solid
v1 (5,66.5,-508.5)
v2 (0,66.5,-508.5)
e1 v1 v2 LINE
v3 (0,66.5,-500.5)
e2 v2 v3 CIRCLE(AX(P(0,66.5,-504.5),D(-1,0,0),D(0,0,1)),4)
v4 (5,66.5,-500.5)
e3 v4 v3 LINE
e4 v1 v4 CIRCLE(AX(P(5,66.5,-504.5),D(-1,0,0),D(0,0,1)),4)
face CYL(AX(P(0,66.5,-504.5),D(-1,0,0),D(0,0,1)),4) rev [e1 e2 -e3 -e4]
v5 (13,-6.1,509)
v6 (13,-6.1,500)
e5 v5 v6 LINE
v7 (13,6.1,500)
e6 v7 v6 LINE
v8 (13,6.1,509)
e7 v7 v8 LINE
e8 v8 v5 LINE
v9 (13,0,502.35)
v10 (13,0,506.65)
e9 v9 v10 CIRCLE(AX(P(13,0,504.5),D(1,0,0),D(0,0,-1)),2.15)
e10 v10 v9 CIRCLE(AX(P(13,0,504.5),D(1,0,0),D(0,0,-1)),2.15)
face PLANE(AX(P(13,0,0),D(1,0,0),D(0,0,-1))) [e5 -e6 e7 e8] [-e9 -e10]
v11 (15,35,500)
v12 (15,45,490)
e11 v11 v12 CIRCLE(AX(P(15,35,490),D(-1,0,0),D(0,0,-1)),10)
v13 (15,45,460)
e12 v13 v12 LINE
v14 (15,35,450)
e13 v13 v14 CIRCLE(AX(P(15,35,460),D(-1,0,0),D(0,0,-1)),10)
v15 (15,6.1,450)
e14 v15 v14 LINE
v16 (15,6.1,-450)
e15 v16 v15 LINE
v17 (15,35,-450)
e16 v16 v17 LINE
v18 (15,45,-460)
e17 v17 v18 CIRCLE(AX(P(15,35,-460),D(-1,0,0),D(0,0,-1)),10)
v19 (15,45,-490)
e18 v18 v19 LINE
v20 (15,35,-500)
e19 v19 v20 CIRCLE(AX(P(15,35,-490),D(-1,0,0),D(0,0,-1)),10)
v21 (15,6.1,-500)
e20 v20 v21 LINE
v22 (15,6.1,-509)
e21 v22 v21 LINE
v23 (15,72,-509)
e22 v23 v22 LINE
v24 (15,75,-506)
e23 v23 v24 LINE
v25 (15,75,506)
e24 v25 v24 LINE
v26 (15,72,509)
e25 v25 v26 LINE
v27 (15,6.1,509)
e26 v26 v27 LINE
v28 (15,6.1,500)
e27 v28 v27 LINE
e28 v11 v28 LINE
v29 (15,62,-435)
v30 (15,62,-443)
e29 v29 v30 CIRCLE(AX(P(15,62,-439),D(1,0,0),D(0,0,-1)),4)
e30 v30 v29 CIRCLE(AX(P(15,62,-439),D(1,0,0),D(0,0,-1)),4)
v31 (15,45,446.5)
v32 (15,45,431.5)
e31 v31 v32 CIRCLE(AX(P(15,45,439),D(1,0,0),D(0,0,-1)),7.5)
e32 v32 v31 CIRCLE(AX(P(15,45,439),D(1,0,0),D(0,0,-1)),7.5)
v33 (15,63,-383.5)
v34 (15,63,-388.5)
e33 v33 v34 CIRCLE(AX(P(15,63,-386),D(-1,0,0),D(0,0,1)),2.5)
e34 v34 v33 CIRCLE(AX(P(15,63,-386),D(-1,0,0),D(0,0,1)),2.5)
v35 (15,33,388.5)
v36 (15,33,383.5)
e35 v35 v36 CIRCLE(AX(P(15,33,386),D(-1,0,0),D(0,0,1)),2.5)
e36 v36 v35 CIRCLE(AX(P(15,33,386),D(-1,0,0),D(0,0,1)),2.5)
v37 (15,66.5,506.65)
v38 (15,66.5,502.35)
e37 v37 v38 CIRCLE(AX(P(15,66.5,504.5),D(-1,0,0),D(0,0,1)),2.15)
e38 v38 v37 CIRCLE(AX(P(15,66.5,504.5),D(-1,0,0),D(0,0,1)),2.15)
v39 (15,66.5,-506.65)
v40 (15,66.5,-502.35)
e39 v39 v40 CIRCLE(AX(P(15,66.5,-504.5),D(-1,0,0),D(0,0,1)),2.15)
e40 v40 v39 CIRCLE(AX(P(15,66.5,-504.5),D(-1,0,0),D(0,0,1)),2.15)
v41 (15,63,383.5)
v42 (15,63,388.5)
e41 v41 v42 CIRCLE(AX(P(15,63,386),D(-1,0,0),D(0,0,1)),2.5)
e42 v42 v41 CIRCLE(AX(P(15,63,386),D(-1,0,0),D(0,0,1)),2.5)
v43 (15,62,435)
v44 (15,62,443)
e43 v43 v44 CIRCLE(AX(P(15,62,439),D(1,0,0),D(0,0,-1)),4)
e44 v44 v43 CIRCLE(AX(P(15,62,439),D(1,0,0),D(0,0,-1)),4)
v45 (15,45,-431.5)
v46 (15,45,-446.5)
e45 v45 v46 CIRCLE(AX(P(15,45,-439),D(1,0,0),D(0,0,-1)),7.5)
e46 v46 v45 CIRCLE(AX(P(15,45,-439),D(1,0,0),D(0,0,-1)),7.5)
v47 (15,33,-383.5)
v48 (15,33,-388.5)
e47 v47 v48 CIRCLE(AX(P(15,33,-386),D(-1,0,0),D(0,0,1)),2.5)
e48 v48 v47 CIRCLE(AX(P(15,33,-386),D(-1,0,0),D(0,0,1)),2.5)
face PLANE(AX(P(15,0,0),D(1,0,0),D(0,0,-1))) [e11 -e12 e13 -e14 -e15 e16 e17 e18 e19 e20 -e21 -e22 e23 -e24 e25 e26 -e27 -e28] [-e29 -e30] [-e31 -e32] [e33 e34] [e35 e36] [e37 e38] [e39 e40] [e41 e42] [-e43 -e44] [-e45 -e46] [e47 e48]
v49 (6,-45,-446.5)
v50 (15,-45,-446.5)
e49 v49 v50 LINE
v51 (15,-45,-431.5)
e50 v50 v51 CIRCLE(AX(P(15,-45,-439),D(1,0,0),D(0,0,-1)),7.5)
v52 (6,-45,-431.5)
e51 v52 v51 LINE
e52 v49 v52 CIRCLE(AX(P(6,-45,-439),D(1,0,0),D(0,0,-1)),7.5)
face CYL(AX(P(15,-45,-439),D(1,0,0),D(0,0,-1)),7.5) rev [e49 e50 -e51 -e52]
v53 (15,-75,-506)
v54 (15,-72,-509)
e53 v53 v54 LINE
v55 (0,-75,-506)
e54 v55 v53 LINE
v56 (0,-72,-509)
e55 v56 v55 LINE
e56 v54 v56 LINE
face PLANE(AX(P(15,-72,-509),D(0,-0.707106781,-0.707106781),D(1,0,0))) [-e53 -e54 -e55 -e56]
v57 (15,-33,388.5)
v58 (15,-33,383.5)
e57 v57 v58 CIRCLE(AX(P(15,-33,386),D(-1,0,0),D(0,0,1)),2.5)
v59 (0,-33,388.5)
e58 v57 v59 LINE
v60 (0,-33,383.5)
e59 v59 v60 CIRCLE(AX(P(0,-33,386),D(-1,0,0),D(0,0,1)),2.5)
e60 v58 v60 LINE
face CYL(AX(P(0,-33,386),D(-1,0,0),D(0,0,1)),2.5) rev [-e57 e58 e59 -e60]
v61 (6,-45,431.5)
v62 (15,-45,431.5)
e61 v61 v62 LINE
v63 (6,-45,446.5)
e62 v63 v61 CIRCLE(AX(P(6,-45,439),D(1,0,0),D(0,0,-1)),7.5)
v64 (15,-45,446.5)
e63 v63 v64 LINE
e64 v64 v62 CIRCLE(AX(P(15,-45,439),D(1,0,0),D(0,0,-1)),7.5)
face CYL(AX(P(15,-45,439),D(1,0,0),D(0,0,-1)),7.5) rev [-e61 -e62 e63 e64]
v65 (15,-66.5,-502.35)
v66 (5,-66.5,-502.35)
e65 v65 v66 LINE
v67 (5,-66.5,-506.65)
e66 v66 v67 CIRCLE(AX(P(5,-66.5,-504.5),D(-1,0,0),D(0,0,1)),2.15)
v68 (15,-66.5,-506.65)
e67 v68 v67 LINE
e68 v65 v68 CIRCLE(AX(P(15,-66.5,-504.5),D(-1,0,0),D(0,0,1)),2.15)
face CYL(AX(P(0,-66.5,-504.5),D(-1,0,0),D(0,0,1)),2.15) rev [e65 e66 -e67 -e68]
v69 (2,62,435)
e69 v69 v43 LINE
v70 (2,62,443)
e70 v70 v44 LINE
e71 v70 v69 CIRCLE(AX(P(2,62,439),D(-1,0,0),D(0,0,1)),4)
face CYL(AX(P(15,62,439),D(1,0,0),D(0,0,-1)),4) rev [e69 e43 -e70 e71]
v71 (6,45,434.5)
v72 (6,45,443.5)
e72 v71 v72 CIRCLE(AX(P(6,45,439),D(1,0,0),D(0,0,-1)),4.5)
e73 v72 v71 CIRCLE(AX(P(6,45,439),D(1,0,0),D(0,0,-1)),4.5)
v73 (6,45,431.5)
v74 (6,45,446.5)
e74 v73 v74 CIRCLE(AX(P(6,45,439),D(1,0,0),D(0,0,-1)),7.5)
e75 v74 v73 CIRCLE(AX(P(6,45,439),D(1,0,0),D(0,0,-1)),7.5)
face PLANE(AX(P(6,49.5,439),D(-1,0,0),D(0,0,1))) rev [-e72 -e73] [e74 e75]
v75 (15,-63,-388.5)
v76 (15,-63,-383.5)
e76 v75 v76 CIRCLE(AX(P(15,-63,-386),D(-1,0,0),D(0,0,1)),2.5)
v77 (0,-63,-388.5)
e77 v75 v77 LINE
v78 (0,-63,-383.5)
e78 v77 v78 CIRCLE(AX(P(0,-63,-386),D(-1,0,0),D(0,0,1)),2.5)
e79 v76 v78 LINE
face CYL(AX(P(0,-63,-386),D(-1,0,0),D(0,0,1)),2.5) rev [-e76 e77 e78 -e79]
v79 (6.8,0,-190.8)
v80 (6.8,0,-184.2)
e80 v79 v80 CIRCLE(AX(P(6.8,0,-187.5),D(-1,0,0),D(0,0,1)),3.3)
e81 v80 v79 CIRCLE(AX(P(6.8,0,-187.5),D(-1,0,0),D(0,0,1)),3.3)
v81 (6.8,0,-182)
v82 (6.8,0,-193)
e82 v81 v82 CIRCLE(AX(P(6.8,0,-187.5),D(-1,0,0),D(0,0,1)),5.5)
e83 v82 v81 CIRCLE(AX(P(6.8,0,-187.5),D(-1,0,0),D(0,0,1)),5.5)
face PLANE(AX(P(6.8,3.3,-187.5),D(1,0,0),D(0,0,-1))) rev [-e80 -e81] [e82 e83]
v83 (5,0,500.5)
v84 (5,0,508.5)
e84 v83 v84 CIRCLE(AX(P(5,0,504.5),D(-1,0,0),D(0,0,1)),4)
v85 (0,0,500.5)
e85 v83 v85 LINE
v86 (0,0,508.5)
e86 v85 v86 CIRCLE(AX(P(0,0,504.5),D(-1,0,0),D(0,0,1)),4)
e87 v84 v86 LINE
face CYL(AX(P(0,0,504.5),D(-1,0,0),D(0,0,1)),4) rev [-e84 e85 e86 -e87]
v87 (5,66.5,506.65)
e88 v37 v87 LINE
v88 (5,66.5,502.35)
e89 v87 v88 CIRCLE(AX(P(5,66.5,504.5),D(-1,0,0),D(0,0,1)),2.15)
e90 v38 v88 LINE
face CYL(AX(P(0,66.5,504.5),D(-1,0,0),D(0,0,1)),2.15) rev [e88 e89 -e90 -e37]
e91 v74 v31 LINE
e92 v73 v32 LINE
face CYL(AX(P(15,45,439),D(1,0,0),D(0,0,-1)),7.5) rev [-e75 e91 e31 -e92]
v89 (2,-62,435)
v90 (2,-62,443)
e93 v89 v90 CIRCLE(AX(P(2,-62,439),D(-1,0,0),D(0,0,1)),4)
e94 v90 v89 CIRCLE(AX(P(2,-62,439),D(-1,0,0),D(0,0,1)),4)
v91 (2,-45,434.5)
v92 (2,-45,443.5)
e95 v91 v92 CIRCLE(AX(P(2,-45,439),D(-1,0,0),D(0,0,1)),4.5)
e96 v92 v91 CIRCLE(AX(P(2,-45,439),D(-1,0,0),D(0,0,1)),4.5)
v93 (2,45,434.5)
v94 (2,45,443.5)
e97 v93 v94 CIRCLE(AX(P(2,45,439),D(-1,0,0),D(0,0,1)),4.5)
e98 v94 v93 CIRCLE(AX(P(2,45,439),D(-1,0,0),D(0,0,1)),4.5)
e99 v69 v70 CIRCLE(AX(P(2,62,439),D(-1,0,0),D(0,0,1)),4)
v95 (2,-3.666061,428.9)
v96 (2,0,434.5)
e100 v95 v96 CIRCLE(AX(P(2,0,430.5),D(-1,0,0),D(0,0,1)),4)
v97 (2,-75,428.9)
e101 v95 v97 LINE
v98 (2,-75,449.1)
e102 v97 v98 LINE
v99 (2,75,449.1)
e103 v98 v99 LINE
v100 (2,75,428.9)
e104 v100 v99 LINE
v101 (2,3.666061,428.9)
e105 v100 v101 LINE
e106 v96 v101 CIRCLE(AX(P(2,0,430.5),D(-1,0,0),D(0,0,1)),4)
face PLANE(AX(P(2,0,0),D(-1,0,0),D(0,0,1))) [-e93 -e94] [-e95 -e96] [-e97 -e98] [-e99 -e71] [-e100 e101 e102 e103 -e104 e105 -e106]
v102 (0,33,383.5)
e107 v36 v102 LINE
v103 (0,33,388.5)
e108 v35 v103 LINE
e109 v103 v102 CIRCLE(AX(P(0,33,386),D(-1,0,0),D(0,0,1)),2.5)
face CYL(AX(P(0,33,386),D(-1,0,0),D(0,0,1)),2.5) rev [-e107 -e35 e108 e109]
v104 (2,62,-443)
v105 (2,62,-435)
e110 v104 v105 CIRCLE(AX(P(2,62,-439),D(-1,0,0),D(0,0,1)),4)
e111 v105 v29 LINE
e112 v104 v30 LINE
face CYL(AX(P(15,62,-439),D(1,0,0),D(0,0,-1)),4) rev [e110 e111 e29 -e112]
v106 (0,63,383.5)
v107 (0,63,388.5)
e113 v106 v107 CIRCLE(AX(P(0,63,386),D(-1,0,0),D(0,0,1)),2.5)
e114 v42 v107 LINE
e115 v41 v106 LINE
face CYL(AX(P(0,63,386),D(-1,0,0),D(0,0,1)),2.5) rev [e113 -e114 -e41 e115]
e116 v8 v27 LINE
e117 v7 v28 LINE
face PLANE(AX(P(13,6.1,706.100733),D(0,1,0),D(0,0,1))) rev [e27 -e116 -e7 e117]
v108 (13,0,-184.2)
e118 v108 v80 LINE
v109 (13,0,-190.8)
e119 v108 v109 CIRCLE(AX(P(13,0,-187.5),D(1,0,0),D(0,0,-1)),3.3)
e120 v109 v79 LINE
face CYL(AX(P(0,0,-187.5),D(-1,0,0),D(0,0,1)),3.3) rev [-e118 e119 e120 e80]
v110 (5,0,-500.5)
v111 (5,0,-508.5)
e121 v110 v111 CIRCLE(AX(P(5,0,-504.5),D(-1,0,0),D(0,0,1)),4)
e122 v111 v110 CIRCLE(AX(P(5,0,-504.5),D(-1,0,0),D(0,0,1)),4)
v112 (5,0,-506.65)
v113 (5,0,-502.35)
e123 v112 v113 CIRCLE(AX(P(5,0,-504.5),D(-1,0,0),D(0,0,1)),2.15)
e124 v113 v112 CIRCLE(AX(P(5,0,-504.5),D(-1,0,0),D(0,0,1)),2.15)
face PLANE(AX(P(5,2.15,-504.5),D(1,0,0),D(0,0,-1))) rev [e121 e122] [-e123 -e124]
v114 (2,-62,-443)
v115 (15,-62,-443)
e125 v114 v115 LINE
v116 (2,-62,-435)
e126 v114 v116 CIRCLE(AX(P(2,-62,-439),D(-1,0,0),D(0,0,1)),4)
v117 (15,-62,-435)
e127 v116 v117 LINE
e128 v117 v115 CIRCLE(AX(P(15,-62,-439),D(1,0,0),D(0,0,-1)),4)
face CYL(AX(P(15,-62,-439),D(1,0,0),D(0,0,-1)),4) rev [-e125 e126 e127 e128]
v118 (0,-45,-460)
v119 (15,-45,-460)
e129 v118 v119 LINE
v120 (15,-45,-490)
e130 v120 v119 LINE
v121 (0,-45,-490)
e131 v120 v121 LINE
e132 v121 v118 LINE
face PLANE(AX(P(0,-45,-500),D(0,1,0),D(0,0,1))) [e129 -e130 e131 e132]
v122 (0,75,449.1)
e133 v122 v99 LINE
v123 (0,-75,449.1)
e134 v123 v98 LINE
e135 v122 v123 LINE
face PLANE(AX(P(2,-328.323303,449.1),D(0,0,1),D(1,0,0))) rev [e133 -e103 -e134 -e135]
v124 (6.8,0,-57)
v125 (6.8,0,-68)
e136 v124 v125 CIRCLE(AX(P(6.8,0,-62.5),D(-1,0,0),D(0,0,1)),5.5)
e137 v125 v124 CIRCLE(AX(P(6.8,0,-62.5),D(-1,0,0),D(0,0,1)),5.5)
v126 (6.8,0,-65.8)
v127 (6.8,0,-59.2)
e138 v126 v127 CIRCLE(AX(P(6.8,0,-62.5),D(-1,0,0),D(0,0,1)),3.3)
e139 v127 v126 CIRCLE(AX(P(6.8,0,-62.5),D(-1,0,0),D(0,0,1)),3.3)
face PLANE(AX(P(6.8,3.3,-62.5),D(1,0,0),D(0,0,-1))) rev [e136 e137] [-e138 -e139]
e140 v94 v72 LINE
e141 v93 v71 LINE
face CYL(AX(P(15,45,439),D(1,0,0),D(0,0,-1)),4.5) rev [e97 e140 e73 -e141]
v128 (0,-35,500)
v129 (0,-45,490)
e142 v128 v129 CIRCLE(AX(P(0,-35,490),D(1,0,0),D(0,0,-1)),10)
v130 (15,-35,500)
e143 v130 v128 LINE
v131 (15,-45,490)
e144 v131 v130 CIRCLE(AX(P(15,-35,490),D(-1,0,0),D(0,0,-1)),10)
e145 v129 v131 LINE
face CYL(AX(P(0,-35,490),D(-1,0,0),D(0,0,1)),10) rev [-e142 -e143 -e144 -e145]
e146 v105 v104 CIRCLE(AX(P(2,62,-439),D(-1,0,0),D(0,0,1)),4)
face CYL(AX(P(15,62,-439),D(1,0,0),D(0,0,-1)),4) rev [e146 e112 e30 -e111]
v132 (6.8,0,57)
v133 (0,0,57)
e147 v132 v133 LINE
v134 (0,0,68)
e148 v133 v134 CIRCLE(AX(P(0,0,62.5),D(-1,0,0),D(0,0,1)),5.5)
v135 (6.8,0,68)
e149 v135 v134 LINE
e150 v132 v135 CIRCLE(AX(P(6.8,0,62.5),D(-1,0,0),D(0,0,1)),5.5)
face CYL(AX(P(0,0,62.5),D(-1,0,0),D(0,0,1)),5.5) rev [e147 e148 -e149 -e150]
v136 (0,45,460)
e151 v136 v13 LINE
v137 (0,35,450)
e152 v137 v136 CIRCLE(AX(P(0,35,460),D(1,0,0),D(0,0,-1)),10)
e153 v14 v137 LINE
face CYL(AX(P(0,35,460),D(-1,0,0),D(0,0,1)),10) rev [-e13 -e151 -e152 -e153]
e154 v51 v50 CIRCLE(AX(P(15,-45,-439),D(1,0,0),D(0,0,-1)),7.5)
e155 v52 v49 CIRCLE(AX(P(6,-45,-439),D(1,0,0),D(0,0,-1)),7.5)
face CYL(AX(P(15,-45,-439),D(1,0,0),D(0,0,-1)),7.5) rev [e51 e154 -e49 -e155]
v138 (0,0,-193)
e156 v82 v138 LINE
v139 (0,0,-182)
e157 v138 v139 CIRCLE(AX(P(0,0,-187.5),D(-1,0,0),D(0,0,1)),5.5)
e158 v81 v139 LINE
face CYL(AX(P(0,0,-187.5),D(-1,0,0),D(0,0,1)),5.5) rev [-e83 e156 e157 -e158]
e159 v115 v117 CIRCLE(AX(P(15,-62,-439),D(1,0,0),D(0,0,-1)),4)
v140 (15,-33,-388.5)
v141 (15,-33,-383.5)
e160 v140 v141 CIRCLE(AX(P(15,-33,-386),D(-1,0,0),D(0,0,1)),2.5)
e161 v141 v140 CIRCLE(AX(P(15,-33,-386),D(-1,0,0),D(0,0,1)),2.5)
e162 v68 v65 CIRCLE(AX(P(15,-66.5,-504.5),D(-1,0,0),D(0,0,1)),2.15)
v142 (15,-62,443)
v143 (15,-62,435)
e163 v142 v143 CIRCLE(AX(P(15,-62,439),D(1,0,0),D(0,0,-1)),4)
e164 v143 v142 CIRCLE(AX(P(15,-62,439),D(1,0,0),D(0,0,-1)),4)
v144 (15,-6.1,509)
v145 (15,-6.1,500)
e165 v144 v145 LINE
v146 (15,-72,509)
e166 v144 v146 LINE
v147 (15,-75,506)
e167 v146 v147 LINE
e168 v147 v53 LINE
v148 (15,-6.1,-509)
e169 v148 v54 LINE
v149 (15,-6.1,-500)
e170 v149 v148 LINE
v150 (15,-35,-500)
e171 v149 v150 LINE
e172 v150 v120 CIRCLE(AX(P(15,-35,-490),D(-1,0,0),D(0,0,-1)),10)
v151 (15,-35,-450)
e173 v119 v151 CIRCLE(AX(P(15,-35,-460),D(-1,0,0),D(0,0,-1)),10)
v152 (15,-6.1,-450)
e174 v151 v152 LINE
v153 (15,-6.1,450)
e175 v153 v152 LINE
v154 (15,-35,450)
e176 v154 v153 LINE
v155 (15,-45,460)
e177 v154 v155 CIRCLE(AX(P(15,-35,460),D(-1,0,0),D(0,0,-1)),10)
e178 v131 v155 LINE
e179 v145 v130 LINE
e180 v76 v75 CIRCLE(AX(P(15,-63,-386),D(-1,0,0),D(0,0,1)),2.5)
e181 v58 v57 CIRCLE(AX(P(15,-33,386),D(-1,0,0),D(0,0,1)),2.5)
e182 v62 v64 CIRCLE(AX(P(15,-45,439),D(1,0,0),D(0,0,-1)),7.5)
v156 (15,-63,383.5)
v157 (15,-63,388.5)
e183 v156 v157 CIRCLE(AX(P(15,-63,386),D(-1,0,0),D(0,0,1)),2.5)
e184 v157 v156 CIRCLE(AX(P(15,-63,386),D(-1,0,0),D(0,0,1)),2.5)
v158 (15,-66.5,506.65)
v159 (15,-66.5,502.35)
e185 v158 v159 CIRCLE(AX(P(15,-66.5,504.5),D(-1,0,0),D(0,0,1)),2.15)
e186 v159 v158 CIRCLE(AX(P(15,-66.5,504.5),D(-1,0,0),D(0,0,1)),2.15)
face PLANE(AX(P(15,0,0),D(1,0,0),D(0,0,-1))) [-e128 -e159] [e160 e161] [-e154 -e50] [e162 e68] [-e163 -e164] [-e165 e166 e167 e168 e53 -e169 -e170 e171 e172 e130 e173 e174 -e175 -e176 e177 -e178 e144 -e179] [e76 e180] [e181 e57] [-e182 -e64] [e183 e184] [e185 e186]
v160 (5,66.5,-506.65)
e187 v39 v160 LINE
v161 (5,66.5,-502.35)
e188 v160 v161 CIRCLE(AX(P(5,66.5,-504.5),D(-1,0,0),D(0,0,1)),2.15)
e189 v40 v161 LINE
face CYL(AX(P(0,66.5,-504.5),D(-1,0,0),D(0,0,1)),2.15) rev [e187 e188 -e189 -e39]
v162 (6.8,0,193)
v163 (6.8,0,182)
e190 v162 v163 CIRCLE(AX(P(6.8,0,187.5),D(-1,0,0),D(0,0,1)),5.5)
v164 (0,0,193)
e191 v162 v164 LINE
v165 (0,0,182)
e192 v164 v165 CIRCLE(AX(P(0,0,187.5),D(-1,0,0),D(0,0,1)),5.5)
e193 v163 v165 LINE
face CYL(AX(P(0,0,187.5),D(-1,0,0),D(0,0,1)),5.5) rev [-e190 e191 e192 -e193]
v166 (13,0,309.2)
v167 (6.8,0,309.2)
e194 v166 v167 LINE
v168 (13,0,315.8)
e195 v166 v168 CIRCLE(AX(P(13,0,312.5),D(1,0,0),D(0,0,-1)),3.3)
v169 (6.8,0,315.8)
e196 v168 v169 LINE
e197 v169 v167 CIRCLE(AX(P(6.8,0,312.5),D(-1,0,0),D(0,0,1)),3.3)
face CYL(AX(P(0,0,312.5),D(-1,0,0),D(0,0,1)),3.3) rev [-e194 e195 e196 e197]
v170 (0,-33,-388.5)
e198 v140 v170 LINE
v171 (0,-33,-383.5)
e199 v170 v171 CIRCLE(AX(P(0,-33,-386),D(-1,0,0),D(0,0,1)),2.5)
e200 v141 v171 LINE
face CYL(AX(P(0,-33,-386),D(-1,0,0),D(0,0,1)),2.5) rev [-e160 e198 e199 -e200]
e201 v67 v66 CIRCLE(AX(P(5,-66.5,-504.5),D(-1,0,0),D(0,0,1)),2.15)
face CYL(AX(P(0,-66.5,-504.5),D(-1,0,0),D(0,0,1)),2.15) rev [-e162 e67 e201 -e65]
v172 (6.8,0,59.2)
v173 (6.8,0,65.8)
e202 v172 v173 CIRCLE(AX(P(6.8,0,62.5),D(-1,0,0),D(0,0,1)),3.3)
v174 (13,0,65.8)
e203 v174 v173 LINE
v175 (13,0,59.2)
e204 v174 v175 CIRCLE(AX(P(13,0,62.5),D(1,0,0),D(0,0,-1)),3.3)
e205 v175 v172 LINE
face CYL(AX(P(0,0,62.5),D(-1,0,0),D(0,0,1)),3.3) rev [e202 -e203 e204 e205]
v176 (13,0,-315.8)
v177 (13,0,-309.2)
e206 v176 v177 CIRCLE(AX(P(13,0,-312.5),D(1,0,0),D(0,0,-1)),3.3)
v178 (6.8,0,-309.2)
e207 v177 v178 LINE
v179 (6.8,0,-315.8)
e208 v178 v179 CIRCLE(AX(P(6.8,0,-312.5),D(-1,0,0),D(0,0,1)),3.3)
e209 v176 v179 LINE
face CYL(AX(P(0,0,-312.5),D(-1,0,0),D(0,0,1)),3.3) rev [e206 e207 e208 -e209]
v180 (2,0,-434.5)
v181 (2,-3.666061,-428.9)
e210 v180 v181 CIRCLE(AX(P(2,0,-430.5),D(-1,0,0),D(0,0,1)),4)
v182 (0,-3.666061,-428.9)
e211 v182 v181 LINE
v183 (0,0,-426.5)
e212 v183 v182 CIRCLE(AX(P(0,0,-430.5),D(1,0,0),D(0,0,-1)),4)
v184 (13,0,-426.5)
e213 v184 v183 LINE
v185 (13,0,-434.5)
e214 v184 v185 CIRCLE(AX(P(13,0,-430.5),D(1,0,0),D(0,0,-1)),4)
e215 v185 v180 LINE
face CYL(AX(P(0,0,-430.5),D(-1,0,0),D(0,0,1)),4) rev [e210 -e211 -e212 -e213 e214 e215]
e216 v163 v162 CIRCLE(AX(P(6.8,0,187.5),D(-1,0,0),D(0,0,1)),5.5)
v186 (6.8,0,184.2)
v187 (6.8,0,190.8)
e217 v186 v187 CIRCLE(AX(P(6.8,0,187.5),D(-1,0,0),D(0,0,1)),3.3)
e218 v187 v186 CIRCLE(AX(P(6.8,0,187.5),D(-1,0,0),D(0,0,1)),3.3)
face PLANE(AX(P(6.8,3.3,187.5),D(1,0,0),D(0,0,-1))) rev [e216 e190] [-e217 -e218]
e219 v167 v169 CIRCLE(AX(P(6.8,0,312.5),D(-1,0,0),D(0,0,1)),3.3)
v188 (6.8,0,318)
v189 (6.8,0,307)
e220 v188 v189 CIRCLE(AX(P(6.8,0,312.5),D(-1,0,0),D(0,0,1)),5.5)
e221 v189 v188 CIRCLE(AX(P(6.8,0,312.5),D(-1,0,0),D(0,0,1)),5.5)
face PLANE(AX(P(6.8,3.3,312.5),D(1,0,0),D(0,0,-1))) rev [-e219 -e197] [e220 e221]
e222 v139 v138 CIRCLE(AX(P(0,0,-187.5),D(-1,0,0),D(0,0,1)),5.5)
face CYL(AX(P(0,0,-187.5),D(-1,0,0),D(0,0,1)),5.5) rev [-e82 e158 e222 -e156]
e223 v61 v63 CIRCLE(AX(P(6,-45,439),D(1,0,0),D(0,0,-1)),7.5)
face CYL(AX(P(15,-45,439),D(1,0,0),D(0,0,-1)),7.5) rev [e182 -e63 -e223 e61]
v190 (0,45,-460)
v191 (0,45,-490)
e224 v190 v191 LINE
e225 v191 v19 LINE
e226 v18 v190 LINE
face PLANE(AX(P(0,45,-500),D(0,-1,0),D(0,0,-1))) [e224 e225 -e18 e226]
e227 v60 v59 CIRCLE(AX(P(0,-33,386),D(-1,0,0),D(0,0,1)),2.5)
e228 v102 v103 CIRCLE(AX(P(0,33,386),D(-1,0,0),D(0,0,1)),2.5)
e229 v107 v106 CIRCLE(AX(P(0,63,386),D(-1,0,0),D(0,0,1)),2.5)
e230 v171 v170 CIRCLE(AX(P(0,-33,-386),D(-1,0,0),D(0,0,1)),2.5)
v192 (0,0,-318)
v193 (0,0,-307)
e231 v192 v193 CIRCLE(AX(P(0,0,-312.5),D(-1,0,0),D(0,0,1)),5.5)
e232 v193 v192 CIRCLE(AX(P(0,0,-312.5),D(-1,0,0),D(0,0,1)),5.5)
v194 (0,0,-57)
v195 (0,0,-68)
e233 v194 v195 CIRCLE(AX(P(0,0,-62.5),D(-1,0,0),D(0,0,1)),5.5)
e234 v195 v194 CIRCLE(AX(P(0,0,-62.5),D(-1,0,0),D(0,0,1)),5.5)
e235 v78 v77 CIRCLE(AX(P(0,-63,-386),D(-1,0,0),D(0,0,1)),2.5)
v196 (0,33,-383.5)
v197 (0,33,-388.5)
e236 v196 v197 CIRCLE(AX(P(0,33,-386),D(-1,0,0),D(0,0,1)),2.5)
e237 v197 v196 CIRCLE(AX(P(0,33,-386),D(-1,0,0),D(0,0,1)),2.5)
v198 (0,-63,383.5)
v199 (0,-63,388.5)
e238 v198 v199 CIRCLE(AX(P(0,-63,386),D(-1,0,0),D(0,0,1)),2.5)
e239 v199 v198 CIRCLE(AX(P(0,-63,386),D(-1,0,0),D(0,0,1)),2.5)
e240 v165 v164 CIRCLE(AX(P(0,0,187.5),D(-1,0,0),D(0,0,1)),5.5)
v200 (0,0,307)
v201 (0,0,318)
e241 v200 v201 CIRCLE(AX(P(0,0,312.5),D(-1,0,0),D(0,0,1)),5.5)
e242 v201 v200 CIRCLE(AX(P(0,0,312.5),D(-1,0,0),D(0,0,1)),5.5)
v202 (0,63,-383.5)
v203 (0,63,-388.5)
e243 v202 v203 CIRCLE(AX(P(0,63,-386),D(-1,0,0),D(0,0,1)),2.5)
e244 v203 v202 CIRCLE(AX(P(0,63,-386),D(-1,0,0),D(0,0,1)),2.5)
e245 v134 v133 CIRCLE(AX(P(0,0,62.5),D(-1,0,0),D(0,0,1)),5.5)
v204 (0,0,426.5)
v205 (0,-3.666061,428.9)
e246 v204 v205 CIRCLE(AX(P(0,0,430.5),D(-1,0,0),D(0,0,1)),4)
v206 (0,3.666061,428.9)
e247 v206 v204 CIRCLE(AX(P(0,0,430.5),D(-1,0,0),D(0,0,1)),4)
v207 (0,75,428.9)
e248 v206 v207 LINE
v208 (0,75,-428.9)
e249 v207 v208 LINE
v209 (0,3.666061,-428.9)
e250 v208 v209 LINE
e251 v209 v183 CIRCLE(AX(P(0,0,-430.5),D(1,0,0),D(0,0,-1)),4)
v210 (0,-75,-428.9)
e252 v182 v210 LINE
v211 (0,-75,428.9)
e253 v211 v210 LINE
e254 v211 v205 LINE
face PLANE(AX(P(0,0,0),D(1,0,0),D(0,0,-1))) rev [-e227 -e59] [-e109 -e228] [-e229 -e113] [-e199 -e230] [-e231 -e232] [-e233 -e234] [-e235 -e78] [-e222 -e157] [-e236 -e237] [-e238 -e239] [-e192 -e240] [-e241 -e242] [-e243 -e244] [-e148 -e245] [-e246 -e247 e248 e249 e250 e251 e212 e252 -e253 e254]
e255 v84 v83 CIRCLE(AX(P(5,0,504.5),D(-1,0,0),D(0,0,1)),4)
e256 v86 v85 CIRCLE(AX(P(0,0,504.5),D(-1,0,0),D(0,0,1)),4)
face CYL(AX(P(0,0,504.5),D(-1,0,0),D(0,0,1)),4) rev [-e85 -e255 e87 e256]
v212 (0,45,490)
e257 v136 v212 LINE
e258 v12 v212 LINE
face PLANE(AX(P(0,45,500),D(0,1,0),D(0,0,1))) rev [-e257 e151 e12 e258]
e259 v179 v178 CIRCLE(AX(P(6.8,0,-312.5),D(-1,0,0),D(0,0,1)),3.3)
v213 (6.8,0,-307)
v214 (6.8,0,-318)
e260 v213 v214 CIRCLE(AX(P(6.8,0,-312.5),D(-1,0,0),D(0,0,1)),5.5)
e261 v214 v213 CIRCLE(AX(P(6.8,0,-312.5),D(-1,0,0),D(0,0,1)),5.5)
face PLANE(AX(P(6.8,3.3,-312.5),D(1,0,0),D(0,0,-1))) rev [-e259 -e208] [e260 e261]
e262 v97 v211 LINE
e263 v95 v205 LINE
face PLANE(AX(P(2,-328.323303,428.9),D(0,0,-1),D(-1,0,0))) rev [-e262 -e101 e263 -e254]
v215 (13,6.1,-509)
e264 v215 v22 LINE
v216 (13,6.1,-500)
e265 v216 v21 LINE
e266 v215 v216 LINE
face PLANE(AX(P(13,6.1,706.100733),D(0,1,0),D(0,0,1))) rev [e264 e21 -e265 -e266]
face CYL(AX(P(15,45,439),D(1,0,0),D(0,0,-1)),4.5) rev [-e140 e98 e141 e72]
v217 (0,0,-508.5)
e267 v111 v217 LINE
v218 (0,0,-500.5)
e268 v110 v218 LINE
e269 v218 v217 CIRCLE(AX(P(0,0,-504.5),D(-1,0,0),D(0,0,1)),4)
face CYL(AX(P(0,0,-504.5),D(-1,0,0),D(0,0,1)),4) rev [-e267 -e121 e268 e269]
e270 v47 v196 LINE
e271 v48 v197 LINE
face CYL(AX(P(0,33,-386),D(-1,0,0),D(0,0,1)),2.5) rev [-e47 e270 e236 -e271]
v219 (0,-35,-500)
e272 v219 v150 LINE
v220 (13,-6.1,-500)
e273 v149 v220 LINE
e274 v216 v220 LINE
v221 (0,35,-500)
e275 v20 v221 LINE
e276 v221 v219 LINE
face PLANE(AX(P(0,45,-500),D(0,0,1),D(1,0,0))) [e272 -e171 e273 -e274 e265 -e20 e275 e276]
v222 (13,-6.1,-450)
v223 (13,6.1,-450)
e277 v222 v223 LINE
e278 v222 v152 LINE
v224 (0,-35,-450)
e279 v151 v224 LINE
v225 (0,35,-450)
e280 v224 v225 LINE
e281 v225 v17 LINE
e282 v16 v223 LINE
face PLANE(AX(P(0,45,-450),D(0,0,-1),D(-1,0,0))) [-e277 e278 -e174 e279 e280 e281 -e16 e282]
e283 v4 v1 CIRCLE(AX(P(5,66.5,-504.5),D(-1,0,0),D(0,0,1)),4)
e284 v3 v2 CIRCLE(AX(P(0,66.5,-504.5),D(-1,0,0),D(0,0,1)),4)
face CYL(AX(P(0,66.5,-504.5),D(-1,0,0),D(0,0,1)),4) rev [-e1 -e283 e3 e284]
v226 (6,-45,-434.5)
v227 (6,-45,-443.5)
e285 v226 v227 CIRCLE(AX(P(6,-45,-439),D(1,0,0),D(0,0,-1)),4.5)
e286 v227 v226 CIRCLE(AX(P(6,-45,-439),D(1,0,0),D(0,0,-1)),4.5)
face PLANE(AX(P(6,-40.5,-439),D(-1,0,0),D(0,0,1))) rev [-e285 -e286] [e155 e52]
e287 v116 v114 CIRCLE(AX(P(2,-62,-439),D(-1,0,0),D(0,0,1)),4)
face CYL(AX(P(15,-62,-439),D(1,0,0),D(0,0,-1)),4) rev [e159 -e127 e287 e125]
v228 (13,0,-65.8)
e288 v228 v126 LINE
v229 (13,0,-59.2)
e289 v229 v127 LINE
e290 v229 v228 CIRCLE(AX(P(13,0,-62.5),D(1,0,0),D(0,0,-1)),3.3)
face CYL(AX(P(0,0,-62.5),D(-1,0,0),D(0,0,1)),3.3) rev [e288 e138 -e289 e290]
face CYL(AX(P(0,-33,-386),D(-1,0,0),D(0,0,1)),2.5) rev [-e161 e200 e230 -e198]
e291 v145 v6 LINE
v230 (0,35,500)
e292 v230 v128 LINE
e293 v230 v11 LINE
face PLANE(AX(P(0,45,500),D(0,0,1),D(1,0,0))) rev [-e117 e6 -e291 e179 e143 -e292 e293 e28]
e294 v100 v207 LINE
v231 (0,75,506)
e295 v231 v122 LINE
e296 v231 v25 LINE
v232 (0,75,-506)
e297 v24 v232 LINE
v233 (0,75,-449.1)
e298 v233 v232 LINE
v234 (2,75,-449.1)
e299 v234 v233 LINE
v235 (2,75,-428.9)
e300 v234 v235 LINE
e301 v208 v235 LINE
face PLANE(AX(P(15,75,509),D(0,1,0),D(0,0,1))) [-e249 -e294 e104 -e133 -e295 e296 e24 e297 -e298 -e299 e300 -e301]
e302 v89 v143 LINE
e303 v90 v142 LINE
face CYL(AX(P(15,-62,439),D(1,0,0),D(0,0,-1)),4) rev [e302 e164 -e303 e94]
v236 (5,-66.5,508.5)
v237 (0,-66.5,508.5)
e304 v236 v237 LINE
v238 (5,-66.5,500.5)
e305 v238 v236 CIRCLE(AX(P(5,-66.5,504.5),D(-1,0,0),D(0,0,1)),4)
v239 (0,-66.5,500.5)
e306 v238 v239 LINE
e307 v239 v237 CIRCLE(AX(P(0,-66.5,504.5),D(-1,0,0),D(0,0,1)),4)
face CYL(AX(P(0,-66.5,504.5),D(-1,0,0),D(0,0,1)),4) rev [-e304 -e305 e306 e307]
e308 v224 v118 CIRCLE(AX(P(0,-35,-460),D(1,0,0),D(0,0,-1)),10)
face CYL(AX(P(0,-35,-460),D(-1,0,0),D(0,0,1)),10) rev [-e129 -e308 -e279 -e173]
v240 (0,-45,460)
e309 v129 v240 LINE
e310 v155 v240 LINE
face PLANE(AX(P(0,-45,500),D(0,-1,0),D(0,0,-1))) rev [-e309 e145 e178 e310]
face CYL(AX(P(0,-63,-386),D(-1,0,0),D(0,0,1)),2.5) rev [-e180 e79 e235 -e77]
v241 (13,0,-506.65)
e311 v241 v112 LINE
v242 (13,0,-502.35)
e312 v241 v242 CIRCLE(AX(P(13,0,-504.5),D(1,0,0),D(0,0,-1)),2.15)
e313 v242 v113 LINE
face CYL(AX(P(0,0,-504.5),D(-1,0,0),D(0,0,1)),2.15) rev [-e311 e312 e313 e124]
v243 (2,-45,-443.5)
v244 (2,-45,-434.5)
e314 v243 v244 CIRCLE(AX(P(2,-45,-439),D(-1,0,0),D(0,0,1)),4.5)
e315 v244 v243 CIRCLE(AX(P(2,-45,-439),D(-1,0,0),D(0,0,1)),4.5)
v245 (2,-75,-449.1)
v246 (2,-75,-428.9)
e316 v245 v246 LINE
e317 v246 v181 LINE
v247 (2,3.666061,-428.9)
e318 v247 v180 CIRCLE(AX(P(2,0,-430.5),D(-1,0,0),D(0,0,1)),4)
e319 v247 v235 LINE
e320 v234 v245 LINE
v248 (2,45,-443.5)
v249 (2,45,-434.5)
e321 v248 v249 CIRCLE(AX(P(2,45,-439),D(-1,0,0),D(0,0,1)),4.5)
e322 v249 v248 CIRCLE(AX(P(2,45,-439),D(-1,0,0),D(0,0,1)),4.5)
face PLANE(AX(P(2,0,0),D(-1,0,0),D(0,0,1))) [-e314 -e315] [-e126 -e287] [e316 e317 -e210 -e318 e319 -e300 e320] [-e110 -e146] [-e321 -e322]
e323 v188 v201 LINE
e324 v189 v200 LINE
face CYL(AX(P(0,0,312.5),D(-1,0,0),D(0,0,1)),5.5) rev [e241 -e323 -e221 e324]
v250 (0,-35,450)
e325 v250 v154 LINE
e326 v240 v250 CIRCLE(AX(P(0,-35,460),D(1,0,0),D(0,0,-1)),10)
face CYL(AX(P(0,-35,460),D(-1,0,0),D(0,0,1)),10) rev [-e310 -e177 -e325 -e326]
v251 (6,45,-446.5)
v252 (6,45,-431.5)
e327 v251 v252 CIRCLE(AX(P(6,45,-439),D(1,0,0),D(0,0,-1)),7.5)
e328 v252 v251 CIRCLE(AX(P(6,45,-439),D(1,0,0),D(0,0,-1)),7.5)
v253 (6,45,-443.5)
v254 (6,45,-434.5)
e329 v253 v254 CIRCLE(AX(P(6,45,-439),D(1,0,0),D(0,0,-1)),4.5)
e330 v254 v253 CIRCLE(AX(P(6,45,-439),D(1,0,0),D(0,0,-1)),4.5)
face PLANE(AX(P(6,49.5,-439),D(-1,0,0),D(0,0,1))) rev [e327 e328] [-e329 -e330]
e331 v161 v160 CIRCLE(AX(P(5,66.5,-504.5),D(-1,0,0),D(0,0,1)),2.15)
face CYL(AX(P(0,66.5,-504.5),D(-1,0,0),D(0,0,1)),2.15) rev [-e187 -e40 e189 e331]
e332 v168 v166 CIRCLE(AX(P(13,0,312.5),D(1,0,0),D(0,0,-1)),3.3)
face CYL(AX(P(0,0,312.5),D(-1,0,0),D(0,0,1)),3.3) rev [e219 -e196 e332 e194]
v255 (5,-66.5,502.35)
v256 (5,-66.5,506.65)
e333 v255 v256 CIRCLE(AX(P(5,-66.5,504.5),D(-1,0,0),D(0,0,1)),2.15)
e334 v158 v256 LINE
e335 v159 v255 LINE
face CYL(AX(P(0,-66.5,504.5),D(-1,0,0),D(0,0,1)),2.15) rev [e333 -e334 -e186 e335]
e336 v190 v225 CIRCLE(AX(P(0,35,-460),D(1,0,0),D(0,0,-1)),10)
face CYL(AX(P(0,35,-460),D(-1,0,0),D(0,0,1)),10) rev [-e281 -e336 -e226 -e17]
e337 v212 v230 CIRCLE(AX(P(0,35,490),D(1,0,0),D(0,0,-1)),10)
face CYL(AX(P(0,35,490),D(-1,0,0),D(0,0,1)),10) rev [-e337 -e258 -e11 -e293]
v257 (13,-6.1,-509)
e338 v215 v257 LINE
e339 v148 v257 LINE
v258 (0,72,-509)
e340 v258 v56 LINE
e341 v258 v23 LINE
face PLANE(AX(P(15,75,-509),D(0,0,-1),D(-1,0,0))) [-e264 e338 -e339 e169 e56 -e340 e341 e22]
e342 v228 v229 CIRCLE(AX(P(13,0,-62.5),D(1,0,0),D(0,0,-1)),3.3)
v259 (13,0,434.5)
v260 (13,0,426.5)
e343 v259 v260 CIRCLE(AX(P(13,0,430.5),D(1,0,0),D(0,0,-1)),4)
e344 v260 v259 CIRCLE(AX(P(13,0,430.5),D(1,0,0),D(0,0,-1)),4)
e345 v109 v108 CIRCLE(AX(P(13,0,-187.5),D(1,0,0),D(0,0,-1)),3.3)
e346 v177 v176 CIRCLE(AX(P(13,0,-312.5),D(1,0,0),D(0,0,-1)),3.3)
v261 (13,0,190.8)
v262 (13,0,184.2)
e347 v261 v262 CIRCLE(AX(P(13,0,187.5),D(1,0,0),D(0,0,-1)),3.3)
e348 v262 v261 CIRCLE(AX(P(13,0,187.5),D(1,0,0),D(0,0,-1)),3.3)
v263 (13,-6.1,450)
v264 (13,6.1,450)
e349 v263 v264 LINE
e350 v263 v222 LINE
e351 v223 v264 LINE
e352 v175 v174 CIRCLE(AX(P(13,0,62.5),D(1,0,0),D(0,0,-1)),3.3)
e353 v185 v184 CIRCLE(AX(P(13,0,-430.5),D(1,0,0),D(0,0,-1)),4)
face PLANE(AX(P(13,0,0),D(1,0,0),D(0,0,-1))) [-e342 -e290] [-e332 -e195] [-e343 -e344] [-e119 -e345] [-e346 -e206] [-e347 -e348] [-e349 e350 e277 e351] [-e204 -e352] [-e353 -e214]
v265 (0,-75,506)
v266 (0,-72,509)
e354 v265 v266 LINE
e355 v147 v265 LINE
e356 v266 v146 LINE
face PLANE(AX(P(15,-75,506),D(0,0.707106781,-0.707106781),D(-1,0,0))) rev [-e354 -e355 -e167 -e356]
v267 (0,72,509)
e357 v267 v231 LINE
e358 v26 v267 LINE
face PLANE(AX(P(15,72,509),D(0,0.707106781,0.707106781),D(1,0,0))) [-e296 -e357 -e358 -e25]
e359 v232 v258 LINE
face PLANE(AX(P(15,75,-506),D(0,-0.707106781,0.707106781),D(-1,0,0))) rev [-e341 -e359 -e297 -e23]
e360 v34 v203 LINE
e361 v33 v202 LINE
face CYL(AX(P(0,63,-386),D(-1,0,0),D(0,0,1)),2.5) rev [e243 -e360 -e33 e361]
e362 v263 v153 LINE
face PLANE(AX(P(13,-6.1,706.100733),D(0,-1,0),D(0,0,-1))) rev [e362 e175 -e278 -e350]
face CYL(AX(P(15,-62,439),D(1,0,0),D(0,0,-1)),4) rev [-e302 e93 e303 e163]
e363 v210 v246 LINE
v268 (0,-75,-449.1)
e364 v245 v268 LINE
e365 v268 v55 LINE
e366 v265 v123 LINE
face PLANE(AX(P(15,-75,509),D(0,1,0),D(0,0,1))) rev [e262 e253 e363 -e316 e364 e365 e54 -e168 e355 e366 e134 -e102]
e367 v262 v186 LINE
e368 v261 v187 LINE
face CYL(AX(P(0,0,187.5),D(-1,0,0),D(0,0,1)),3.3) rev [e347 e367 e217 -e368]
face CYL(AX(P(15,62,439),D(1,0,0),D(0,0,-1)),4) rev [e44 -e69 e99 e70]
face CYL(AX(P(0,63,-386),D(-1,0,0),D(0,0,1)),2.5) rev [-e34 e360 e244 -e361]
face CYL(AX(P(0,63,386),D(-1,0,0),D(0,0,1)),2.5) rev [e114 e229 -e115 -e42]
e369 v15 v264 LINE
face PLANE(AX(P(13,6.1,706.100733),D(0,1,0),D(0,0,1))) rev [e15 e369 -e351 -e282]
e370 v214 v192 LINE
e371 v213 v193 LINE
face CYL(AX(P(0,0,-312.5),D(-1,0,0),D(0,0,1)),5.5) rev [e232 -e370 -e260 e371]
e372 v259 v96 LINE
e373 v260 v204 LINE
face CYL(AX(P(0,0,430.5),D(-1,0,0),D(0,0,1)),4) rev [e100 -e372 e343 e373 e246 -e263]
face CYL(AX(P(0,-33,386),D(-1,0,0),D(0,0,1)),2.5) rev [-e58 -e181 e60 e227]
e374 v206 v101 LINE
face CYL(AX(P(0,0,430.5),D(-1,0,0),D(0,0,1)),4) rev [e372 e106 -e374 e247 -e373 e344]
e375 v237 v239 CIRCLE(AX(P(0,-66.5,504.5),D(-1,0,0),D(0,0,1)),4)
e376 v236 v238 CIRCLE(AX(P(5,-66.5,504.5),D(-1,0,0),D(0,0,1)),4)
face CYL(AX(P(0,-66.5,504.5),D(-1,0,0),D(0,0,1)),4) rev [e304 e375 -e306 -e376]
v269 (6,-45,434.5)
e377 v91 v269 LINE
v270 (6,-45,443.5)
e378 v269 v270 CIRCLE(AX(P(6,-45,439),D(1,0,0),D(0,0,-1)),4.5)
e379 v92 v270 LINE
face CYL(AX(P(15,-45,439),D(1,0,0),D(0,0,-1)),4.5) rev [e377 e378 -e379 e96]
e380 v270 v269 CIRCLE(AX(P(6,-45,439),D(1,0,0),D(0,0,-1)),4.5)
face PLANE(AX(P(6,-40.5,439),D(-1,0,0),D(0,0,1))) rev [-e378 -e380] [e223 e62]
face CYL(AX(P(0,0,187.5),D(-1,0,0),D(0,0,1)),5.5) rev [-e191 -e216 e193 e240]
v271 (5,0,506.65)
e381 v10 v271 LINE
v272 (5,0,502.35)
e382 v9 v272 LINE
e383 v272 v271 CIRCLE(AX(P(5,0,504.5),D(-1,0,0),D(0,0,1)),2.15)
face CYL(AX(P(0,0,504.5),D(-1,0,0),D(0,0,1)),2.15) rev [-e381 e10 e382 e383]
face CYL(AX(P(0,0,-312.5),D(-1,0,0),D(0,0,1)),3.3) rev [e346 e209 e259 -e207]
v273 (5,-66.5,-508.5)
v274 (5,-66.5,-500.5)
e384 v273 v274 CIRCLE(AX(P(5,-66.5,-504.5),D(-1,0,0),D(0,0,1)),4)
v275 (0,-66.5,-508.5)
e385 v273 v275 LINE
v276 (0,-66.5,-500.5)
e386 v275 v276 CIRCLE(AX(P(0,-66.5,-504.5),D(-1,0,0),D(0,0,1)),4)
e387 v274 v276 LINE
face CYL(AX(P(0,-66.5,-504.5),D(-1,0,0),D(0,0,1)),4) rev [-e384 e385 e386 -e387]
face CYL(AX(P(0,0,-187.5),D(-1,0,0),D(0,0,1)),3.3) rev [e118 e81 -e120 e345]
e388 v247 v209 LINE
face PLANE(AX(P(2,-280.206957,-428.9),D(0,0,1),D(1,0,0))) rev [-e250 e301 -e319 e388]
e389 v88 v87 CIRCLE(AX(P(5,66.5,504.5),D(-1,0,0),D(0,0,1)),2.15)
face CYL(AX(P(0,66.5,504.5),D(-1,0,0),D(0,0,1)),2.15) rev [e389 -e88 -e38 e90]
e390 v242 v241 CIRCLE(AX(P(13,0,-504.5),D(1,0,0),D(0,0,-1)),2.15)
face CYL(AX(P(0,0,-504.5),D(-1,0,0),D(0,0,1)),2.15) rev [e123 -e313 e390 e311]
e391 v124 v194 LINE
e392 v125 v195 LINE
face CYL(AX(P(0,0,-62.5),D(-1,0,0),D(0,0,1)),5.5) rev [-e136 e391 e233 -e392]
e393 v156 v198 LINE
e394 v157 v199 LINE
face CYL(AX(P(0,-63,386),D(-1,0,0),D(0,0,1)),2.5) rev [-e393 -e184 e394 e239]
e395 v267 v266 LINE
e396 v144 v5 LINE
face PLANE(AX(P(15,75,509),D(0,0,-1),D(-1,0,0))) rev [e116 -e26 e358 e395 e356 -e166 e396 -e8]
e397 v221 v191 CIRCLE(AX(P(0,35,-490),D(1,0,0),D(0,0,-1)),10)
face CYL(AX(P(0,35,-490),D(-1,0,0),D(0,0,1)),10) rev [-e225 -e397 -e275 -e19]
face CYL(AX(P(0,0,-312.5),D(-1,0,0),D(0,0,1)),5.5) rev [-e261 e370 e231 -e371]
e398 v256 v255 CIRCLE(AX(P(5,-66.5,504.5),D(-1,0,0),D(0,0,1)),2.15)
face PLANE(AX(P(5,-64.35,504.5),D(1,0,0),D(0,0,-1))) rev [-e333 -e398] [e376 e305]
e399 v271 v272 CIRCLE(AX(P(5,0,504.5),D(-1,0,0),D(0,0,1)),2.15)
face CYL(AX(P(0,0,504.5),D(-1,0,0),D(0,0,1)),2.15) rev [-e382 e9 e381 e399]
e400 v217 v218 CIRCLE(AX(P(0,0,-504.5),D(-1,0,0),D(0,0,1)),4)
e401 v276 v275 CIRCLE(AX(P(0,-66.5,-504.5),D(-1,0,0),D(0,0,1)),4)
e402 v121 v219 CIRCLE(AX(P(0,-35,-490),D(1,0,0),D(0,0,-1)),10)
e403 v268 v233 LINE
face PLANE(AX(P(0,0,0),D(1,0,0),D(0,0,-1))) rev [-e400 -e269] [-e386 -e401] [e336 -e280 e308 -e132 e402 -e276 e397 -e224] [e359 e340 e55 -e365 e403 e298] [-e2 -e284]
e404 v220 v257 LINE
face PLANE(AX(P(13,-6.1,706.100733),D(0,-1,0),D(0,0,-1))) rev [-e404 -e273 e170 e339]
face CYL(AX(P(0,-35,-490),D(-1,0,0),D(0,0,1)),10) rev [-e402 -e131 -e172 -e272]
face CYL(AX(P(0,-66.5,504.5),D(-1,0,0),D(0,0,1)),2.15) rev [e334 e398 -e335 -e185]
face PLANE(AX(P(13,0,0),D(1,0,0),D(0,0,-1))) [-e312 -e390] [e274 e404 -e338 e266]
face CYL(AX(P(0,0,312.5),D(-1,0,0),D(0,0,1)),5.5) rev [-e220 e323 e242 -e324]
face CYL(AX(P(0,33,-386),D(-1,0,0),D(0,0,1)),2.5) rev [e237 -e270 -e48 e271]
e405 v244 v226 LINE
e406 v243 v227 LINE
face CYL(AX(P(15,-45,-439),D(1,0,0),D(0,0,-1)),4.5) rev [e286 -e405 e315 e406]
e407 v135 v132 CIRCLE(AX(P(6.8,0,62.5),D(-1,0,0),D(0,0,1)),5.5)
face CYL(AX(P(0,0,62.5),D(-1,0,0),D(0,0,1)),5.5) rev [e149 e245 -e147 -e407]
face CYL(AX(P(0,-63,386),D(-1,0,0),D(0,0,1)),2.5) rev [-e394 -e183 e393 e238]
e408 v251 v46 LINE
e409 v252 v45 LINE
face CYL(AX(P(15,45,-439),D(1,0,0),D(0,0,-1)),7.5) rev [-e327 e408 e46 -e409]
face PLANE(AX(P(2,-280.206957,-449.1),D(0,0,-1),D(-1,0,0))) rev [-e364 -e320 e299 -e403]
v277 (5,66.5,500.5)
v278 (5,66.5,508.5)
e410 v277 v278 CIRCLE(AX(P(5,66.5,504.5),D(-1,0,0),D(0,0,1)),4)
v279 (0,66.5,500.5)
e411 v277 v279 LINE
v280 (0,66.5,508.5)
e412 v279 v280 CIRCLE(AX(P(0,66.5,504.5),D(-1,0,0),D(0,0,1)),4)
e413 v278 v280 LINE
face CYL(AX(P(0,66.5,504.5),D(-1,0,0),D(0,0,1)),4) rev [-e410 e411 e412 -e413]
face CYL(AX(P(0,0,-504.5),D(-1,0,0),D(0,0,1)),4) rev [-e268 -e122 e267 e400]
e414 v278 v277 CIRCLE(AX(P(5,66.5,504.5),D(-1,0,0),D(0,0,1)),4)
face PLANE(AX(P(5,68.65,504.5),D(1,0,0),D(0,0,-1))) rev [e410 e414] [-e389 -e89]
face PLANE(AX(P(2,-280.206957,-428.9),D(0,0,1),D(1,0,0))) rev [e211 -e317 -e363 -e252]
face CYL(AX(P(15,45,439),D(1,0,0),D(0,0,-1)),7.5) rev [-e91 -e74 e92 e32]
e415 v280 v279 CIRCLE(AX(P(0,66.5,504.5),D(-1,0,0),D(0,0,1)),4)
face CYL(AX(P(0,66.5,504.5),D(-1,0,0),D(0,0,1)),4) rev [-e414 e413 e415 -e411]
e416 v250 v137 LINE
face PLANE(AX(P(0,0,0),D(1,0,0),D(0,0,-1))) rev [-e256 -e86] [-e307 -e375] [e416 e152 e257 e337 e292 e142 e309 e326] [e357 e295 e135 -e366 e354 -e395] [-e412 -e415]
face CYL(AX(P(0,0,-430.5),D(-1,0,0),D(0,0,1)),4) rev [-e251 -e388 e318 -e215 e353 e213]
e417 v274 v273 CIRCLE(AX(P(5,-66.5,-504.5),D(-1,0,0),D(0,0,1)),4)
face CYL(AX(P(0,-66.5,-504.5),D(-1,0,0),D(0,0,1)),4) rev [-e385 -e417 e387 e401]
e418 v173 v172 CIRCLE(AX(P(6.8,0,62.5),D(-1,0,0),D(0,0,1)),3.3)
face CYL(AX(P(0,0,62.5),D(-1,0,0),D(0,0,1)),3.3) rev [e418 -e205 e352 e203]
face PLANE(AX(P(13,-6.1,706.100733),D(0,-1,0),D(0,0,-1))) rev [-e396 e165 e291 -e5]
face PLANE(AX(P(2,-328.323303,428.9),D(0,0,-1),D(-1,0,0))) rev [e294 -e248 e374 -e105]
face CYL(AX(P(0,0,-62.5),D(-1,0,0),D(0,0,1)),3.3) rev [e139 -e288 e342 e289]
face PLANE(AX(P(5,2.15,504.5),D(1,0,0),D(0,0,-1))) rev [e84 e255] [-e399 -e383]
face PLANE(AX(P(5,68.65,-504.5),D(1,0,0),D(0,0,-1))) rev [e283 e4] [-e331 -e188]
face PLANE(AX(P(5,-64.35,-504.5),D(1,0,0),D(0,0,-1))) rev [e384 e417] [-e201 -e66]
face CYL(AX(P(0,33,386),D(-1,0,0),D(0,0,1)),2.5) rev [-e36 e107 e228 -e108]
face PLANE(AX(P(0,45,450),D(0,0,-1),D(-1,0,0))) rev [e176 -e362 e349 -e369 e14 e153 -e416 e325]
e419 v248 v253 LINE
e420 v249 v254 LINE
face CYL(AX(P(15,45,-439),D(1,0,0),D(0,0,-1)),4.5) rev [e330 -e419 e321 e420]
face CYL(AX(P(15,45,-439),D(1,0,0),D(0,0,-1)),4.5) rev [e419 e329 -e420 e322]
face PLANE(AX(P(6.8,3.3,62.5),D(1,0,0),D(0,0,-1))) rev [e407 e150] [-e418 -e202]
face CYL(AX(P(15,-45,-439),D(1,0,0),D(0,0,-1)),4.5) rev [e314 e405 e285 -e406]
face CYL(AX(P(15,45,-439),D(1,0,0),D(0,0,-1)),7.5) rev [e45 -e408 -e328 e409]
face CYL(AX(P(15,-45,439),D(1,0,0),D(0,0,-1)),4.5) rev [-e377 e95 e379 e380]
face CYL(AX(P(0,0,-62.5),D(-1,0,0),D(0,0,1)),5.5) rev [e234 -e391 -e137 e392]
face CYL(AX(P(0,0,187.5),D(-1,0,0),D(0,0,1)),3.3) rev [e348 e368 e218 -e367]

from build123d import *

# Parameters (mm, degrees)
SKETCH_1_W                  = 1018
SKETCH_1_H                  = 150
EXTRUDE_1_DEPTH             = 15
SKETCH_2_W                  = 1412.201465812
SKETCH_2_H                  = 12.2
CUT_EXTRUDE_1_DEPTH         = 2
SKETCH_15_W                 = 20.2
SKETCH_15_H                 = 532.053707348
SKETCH_15_H_2               = 612.26589084
CUT_EXTRUDE_4_DEPTH         = 2
CHAMFER_1_SIZE              = 3
SKETCH_24_W                 = 50
SKETCH_24_H                 = 90
CUT_EXTRUDE_5_DEPTH         = 515.714483962
FILLET_2_R                  = 10
FILLET_2_OF_MIRROR_1_R      = 10
HOLE_WIZARD_9_D             = 9
HOLE_WIZARD_9_CBORE_D       = 15
HOLE_WIZARD_9_CBORE_DEPTH   = 9
MM_2_AT_2_COUNT             = 2
MM_2_AT_2_PITCH             = 124
HOLE_WIZARD_M6_1_D          = 5
HOLE_WIZARD_9_2_D           = 6.6
HOLE_WIZARD_9_2_CBORE_D     = 11
HOLE_WIZARD_9_2_CBORE_DEPTH = 6.8
MM_3_D                      = 8
HOLE_WIZARD_0_D             = 4.3
HOLE_WIZARD_0_CBORE_D       = 8
HOLE_WIZARD_0_CBORE_DEPTH   = 5


with BuildPart() as part:
    # 草图1 → 凸台-拉伸1 (new body)
    with BuildSketch(Plane(origin=(0, 0, 0), x_dir=(0, 0, -1), z_dir=(1, 0, 0))):
        Rectangle(SKETCH_1_W, SKETCH_1_H)
    extrude(amount=EXTRUDE_1_DEPTH)

    # 草图2 → 切除-拉伸1 (cut)
    with BuildSketch(Plane(origin=(15, 0, 0), x_dir=(0, 0, -1), z_dir=(1, 0, 0))):
        Rectangle(SKETCH_2_W, SKETCH_2_H)
    extrude(amount=-CUT_EXTRUDE_1_DEPTH, mode=Mode.SUBTRACT)

    # 草图15 → 切除-拉伸4 (cut)
    with BuildSketch(Plane.ZY):
        with Locations((-439, -14.180103386)):
            Rectangle(SKETCH_15_W, SKETCH_15_H)
        with Locations((439, -22.190357802)):
            Rectangle(SKETCH_15_W, SKETCH_15_H_2)
    extrude(amount=-CUT_EXTRUDE_4_DEPTH, mode=Mode.SUBTRACT)

    # 倒角1
    chamfer_1_edges = [part.edges().sort_by_distance(p)[0] for p in [
        (7.5, 75, 509),
        (7.5, 75, -509),
        (7.5, -75, -509),
        (7.5, -75, 509),
    ]]
    chamfer(chamfer_1_edges, length=CHAMFER_1_SIZE)

    # 草图24 → 切除-拉伸5 (cut, through all)
    with BuildSketch(Plane(origin=(15, 0, 0), x_dir=(0, 0, -1), z_dir=(1, 0, 0))):
        with Locations((-475, 0)):
            Rectangle(SKETCH_24_W, SKETCH_24_H)
    cut_extrude_5 = extrude(amount=-CUT_EXTRUDE_5_DEPTH, mode=Mode.SUBTRACT)

    # 圆角2
    fillet_2_edges = [part.edges().sort_by_distance(p)[0] for p in [
        (7.5, 45, 450),
        (7.5, -45, 500),
        (7.5, -45, 450),
        (7.5, 45, 500),
    ]]
    fillet(fillet_2_edges, radius=FILLET_2_R)

    # 镜向1: 切除-拉伸5 across plane
    add(cut_extrude_5.mirror(Plane.XY), mode=Mode.SUBTRACT)

    # 圆角2 of 镜向1
    fillet_2_of_mirror_1_edges = [part.edges().sort_by_distance(p)[0] for p in [
        (7.5, 45, -450),
        (7.5, -45, -500),
        (7.5, -45, -450),
        (7.5, 45, -500),
    ]]
    fillet(fillet_2_of_mirror_1_edges, radius=FILLET_2_OF_MIRROR_1_R)

    # Hole Wizard 9 (through all)
    with Locations(Plane(origin=(15, 0, 0), x_dir=(0, 0, -1), z_dir=(1, 0, 0))):
        with Locations((439, 45), (439, -45)):
            hole_wizard_9 = CounterBoreHole(HOLE_WIZARD_9_D / 2, HOLE_WIZARD_9_CBORE_D / 2, HOLE_WIZARD_9_CBORE_DEPTH)

    # 草图34 → 大小mm 暗销孔2 (revolve, cut)
    with BuildSketch(Plane(origin=(15, 62, -439), x_dir=(0, 0, -1), z_dir=(0, 1, 0))):
        Polygon((0, 0), (0, 17.403442476), (4, 15), (4, 0), align=None)
    mm_2 = revolve(axis=Axis((21.35, 62, -439), (-1, 0, 0)), mode=Mode.SUBTRACT)

    # 大小mm 暗销孔2 at 2: 大小mm 暗销孔2 ×2
    with Locations(*[(0, -i * MM_2_AT_2_PITCH, 0) for i in range(1, MM_2_AT_2_COUNT)]):
        add(mm_2, mode=Mode.SUBTRACT)

    # M6 螺纹孔1 (through all)
    with Locations(Plane.ZY):
        with Locations((-386, 63), (-386, 33), (-386, -33), (-386, -63)):
            hole_wizard_m6_1 = Hole(HOLE_WIZARD_M6_1_D / 2)

    # Hole Wizard 9 2 (through all)
    with Locations(Plane.ZY):
        with Locations((-312.5, 0), (-187.5, 0), (-62.5, 0), (62.5, 0), (187.5, 0), (312.5, 0)):
            CounterBoreHole(HOLE_WIZARD_9_2_D / 2, HOLE_WIZARD_9_2_CBORE_D / 2, HOLE_WIZARD_9_2_CBORE_DEPTH)

    # 大小mm 暗销孔3 (through all)
    with Locations(Plane.ZY):
        with Locations((430.5, 0), (-430.5, 0)):
            mm_3 = Hole(MM_3_D / 2)

    # 打孔尺寸(%根据)内六角圆柱头螺钉的类型0 (through all)
    with Locations(Plane.ZY):
        with Locations((-504.5, 66.5), (-504.5, 0), (-504.5, -66.5)):
            hole_wizard_0 = CounterBoreHole(HOLE_WIZARD_0_D / 2, HOLE_WIZARD_0_CBORE_D / 2, HOLE_WIZARD_0_CBORE_DEPTH)

    # 镜向2: Hole Wizard 9, 大小mm 暗销孔2, M6 螺纹孔1, 大小mm 暗销孔3, 打孔尺寸(%根据)内六角圆柱头螺钉的类型0 across plane
    add(hole_wizard_9.mirror(Plane.XY), mode=Mode.SUBTRACT)
    add(mm_2.mirror(Plane.XY), mode=Mode.SUBTRACT)
    add(hole_wizard_m6_1.mirror(Plane.XY), mode=Mode.SUBTRACT)
    add(mm_3.mirror(Plane.XY), mode=Mode.SUBTRACT)
    add(hole_wizard_0.mirror(Plane.XY), mode=Mode.SUBTRACT)

    # 镜向2 copy 1 sketch → 镜向2 copy 1 (revolve, cut)
    with BuildSketch(Plane(origin=(15, -62, 439), x_dir=(0, 0, 1), z_dir=(0, 1, 0))):
        Polygon((0, 0), (0, -17.403442476), (4, -15), (4, 0), align=None)
    revolve(axis=Axis((21.35, -62, 439), (1, 0, 0)), mode=Mode.SUBTRACT)


solid = part.part
